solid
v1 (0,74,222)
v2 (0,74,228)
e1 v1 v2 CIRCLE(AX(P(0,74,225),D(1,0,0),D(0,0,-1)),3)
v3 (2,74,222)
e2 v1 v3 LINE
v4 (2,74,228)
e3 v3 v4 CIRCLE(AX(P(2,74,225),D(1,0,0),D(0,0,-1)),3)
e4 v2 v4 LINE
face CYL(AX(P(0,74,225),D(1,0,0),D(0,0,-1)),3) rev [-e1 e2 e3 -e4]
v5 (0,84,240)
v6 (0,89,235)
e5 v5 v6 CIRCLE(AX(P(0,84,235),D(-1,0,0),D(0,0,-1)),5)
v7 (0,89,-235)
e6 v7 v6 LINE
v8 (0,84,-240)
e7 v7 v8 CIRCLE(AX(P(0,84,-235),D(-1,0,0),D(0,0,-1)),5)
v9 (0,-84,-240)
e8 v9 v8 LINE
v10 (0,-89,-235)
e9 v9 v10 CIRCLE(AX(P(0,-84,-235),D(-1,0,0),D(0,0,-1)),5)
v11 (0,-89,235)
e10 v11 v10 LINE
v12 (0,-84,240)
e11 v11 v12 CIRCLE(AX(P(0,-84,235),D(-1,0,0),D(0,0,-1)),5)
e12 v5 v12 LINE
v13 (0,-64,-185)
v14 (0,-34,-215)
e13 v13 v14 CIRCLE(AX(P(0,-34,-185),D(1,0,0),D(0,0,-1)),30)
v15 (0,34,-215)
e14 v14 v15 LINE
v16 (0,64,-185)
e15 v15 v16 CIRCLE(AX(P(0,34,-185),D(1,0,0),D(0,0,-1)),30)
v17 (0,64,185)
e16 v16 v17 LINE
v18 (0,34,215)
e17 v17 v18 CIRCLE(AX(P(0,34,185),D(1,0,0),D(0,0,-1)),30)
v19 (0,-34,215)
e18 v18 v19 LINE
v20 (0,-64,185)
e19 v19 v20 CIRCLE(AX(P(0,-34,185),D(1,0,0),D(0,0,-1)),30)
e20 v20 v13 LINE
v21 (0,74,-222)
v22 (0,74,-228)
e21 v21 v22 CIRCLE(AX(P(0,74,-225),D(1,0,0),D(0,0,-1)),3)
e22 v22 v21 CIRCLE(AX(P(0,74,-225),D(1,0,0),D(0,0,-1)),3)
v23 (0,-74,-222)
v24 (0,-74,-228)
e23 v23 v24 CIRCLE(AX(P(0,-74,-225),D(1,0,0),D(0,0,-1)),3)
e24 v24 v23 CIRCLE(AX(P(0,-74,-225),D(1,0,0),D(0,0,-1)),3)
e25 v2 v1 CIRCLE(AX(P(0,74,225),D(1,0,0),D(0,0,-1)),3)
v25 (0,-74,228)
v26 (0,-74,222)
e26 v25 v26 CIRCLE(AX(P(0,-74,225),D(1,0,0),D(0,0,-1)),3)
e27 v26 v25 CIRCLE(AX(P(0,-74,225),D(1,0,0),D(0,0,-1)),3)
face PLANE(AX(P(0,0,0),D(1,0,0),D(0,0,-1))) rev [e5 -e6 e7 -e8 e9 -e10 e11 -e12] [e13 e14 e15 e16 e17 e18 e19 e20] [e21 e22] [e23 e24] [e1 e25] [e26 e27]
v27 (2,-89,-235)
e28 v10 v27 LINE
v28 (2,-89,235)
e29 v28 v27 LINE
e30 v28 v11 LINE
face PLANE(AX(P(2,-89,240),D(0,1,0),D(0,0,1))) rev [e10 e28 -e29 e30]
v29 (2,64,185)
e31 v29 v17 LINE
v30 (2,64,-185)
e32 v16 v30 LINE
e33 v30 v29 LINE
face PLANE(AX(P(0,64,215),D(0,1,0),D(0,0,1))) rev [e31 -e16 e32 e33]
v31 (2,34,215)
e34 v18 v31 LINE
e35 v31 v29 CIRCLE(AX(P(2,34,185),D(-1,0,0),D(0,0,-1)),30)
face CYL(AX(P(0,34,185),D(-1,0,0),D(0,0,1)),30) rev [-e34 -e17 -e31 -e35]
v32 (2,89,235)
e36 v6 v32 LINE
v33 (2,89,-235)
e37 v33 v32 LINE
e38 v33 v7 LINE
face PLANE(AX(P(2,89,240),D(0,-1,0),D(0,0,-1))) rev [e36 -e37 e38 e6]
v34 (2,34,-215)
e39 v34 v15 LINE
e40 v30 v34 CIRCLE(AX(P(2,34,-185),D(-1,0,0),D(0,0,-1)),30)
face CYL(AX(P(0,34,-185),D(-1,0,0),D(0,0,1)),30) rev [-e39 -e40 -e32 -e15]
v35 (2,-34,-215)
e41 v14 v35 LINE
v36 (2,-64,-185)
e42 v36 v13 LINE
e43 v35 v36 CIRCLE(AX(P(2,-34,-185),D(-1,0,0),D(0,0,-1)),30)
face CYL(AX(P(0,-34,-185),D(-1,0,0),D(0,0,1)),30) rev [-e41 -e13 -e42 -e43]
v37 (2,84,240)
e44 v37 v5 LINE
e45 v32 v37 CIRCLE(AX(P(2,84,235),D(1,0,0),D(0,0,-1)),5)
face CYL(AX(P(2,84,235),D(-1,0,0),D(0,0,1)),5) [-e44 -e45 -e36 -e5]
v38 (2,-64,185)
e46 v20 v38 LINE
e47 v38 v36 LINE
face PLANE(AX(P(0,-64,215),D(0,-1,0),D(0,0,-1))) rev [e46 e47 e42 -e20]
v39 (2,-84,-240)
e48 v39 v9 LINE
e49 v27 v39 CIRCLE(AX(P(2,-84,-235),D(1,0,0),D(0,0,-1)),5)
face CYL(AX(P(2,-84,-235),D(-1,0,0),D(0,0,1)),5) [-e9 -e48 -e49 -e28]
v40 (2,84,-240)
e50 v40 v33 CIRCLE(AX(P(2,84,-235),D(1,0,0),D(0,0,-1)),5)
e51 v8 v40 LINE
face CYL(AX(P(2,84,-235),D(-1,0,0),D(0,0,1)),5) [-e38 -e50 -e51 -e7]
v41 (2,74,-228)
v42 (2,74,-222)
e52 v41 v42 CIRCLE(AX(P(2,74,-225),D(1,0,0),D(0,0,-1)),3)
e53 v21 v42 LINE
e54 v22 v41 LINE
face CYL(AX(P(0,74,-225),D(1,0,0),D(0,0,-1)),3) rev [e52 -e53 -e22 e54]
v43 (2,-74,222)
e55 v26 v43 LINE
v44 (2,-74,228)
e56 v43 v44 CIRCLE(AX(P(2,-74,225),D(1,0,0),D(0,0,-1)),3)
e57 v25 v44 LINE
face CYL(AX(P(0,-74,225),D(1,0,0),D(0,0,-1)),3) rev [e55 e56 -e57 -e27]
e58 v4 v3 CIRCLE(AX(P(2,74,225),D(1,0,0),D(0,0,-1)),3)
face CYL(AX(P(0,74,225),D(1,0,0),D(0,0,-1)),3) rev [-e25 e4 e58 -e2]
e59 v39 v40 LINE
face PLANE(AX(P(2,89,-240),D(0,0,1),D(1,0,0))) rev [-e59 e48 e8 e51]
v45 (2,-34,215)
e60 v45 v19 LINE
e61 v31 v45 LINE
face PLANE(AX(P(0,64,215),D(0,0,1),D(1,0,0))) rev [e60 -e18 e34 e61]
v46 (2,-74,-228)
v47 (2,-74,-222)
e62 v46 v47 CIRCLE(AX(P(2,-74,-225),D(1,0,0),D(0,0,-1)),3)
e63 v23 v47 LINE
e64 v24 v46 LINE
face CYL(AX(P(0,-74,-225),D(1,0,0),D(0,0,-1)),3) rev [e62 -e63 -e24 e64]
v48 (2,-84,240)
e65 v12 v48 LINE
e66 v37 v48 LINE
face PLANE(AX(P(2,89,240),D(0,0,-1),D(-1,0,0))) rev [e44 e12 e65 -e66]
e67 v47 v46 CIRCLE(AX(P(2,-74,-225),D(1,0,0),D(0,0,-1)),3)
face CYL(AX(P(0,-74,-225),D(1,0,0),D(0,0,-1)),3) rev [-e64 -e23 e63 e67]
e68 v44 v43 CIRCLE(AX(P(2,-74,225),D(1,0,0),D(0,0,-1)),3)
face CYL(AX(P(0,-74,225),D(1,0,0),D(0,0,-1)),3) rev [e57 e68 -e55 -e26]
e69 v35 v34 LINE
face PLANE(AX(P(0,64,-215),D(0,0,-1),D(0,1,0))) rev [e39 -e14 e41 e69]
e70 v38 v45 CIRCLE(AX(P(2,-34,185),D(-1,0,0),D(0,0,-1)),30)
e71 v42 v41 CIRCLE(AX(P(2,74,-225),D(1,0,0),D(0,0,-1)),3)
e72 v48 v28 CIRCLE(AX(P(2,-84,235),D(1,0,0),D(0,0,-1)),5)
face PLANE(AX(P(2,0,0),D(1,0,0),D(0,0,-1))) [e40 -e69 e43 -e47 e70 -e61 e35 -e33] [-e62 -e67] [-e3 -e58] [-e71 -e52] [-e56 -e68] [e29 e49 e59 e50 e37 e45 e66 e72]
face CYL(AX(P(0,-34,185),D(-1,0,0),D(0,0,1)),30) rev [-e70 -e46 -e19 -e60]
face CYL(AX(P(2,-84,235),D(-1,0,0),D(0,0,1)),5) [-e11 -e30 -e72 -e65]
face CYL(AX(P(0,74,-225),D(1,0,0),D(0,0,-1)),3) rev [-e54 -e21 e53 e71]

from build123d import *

# Parameters (mm, degrees)
SKETCH_1_W          = 480
SKETCH_1_H          = 178
EXTRUDE_1_DEPTH     = 2
SKETCH_2_R          = 3
CUT_EXTRUDE_1_DEPTH = 256.978514723
FILLET_1_R          = 5
SKETCH_3_W          = 430
SKETCH_3_H          = 128
CUT_EXTRUDE_2_DEPTH = 256.978514723
FILLET_2_R          = 30


with BuildPart() as part:
    # 草图1 → 凸台-拉伸1 (new body)
    with BuildSketch(Plane(origin=(0, 0, 0), x_dir=(0, 0, -1), z_dir=(1, 0, 0))):
        Rectangle(SKETCH_1_W, SKETCH_1_H)
    extrude(amount=EXTRUDE_1_DEPTH)

    # 草图2 → 切除-拉伸1 (cut, through all)
    with BuildSketch(Plane(origin=(2, 0, 0), x_dir=(0, 0, -1), z_dir=(1, 0, 0))):
        with Locations((-225, 74)):
            Circle(SKETCH_2_R)
        with Locations((225, 74)):
            Circle(SKETCH_2_R)
        with Locations((-225, -74)):
            Circle(SKETCH_2_R)
        with Locations((225, -74)):
            Circle(SKETCH_2_R)
    extrude(amount=-CUT_EXTRUDE_1_DEPTH, mode=Mode.SUBTRACT)

    # 圆角1
    fillet_1_edges = [part.edges().sort_by_distance(p)[0] for p in [
        (1, 89, 240),
        (1, 89, -240),
        (1, -89, -240),
        (1, -89, 240),
    ]]
    fillet(fillet_1_edges, radius=FILLET_1_R)

    # 草图3 → 切除-拉伸2 (cut, through all)
    with BuildSketch(Plane(origin=(2, 0, 0), x_dir=(0, 0, -1), z_dir=(1, 0, 0))):
        Rectangle(SKETCH_3_W, SKETCH_3_H)
    extrude(amount=-CUT_EXTRUDE_2_DEPTH, mode=Mode.SUBTRACT)

    # 圆角2
    fillet_2_edges = [part.edges().sort_by_distance(p)[0] for p in [
        (1, -64, 215),
        (1, 64, 215),
        (1, 64, -215),
        (1, -64, -215),
    ]]
    fillet(fillet_2_edges, radius=FILLET_2_R)


solid = part.part
